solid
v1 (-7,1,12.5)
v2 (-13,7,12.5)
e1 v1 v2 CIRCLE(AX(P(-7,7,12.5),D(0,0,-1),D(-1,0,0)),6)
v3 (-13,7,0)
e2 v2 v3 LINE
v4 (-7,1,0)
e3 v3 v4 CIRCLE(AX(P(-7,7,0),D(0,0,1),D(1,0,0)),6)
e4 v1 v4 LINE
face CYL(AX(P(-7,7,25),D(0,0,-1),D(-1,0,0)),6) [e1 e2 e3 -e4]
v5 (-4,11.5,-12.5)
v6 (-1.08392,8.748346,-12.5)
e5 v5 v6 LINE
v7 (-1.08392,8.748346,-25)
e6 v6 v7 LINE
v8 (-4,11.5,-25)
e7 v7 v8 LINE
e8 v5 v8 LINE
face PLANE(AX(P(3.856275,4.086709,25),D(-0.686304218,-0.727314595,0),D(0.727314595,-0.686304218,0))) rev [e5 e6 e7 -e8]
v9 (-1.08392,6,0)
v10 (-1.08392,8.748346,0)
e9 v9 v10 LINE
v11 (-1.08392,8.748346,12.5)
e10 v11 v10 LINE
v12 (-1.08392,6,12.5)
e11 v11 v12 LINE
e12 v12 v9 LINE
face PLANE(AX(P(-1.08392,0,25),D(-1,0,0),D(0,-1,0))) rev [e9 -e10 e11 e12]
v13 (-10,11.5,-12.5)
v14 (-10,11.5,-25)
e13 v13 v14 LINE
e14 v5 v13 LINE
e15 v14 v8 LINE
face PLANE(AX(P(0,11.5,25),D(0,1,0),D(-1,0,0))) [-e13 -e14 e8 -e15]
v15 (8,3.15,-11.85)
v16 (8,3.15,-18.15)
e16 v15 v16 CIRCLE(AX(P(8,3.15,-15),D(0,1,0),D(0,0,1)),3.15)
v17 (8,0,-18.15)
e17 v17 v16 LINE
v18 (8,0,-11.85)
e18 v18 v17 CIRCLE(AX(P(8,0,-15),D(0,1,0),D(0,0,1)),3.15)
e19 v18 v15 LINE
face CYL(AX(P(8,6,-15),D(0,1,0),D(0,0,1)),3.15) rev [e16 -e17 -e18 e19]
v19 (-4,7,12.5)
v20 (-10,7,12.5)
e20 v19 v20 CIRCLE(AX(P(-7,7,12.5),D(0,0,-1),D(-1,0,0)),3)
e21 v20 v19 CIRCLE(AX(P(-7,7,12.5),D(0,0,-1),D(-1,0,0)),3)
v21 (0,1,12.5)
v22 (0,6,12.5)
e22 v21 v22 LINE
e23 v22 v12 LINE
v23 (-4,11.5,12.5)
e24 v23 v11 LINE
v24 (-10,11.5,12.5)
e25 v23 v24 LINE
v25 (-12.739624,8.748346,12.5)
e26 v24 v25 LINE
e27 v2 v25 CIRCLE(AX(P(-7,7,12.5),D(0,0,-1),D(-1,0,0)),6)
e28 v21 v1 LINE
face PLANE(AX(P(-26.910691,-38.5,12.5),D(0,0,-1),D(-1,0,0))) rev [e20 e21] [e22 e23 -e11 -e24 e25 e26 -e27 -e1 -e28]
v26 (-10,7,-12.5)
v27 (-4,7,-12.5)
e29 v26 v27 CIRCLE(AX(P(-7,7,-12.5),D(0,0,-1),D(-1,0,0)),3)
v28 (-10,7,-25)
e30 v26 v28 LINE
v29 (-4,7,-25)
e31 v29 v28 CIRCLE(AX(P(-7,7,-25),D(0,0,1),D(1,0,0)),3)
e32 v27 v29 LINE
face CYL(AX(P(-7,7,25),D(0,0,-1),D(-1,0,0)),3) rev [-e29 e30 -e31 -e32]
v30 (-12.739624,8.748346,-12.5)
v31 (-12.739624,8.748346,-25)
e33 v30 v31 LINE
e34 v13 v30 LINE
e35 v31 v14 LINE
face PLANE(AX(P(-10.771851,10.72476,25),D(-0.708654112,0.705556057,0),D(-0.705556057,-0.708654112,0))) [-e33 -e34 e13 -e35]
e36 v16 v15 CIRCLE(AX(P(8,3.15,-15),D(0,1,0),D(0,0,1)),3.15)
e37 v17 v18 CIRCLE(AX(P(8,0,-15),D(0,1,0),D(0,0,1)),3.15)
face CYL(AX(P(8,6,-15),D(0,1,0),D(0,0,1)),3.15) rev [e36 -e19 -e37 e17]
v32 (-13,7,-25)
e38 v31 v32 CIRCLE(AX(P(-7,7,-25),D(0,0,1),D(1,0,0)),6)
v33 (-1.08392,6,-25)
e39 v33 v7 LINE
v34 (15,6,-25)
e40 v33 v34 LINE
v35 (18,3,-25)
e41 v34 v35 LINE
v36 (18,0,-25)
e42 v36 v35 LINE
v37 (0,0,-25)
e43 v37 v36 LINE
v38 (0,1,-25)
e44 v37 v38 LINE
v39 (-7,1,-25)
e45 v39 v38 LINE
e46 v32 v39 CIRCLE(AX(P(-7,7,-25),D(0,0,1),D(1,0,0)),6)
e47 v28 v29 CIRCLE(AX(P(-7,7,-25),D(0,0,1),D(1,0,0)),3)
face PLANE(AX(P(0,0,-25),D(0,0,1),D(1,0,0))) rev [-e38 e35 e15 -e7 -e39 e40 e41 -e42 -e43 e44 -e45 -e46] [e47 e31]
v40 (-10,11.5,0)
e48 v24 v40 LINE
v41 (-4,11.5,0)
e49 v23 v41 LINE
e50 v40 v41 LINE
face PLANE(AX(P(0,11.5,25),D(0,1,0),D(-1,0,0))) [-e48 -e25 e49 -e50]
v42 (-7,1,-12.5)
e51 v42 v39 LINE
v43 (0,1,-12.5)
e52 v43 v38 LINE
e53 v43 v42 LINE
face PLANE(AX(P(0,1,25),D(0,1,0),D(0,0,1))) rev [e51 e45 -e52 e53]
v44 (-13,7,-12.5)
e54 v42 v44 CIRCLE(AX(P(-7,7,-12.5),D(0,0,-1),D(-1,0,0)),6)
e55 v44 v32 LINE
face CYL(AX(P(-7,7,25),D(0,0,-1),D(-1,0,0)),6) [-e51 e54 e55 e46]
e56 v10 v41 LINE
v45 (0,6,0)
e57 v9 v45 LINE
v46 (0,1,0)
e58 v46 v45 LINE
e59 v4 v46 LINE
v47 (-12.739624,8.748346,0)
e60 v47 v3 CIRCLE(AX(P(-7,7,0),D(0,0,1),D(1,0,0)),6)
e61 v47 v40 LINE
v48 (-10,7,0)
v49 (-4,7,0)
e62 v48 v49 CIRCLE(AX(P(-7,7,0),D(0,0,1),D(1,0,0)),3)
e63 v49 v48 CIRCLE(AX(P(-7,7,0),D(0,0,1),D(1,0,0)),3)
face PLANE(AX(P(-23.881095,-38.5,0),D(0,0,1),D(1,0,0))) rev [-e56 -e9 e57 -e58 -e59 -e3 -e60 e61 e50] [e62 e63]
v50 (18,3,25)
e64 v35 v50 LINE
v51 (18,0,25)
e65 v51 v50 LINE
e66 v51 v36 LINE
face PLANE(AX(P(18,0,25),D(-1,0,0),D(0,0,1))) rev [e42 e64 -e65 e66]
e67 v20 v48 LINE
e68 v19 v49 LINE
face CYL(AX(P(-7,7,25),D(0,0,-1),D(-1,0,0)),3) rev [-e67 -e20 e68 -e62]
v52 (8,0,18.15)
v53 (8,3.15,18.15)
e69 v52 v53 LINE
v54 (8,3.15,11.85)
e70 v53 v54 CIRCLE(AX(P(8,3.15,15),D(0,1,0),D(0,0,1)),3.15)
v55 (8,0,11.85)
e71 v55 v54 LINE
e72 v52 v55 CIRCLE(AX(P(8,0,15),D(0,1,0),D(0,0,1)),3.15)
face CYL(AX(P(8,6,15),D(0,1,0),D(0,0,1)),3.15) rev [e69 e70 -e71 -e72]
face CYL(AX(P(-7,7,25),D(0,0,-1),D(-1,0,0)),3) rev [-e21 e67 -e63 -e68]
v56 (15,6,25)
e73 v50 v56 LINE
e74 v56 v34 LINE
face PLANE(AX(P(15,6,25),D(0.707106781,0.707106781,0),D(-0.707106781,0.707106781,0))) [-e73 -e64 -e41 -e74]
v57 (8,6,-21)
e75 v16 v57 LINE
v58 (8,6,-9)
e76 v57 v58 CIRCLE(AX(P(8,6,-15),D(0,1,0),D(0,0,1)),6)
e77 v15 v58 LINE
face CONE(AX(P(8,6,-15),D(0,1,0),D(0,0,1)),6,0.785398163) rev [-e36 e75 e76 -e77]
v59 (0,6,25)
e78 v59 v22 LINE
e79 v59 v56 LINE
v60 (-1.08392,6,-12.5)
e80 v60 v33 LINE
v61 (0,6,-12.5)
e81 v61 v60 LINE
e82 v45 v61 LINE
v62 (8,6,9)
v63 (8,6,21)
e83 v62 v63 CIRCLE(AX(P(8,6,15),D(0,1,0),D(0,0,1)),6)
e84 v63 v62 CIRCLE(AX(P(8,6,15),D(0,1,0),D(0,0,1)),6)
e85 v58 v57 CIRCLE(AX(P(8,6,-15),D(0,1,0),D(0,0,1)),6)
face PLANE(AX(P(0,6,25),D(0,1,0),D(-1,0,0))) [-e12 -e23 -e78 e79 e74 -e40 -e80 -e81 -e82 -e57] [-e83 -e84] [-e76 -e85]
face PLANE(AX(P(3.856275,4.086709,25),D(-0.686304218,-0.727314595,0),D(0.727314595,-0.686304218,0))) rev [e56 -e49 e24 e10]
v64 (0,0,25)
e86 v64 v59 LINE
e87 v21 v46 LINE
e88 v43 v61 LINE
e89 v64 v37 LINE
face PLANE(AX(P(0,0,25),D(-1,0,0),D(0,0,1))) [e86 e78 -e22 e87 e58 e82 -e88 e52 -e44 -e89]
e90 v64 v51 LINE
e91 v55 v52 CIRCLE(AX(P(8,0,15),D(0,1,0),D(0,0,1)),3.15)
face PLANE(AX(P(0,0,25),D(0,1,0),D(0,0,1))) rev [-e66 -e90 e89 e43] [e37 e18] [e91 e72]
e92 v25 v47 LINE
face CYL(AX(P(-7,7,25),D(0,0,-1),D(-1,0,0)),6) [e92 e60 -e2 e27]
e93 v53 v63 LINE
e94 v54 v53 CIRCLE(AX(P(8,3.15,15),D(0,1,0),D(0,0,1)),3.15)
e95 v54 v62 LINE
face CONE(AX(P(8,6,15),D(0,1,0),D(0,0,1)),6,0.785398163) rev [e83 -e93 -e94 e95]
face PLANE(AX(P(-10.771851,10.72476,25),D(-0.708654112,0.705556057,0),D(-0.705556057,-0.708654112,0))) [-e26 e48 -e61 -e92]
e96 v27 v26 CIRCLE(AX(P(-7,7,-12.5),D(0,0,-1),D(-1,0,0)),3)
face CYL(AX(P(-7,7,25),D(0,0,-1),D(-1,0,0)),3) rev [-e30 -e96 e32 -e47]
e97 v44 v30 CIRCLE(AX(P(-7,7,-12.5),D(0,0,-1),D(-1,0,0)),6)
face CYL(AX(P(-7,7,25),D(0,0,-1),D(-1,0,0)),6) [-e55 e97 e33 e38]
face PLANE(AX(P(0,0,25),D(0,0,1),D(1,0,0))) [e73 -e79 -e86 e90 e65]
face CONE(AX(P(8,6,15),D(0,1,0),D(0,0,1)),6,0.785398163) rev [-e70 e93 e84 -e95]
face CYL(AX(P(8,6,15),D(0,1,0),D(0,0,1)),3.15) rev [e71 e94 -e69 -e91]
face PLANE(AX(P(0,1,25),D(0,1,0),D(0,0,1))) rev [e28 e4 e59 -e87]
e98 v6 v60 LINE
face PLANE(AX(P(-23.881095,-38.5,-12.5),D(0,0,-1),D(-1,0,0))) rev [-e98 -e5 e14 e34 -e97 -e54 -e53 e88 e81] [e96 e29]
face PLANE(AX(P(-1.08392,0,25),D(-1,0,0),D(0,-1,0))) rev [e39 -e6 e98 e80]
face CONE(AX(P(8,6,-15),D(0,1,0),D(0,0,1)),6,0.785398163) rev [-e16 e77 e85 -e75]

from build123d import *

# Parameters (mm, degrees)
SKETCH_1_R                = 3
EXTRUDE_1_DEPTH           = 25
CHAMFER_1_SIZE            = 3
SKETCH_2_R                = 1.072137289
CUT_EXTRUDE_1_DEPTH       = 50
HOLE_WIZARD_1_D           = 6.3
HOLE_WIZARD_1_CSINK_D     = 12
HOLE_WIZARD_1_CSINK_ANGLE = 90
SKETCH_4_W                = 23.881095176
SKETCH_4_H                = 12.5
SKETCH_4_W_2              = 26.910691004
CUT_EXTRUDE_2_DEPTH       = 50


with BuildPart() as part:
    # 草图1 → 拉伸1 (new, symmetric)
    with BuildSketch(Plane.XY):
        with BuildLine():
            Line((-7, 1), (0, 1))
            Line((0, 1), (0, 0))
            Line((0, 0), (18, 0))
            Line((18, 0), (18, 6))
            Line((18, 6), (-1.083920217, 6))
            Line((-1.083920217, 6), (-1.083920217, 8.748346358))
            Line((-1.083920217, 8.748346358), (-4, 11.5))
            Line((-4, 11.5), (-10, 11.5))
            Line((-10, 11.5), (-12.739624118, 8.748346358))
            ThreePointArc((-12.739624118, 8.748346358), (-11.821310929, 3.428591185), (-7, 1))
        make_face()
        with Locations((-7, 7)):
            Circle(SKETCH_1_R, mode=Mode.SUBTRACT)
    extrude(amount=EXTRUDE_1_DEPTH, both=True)

    # 倒角1
    chamfer_1_edges = [part.edges().sort_by_distance(p)[0] for p in [
        (18, 6, 0),
    ]]
    chamfer(chamfer_1_edges, length=CHAMFER_1_SIZE)

    # 草图2 → 切除-拉伸1 (cut)
    with BuildSketch(Plane(origin=(0, 6, 0), x_dir=(1, 0, 0), z_dir=(0, 1, 0))):
        with Locations(Location((8, 15, 0), (0, 0, 180))):
            Circle(SKETCH_2_R)
        with Locations(Location((8, -15, 0), (0, 0, 270))):
            Circle(SKETCH_2_R)
    extrude(amount=-CUT_EXTRUDE_1_DEPTH, mode=Mode.SUBTRACT)

    # 打孔尺寸开槽半沉头螺钉的类型1 (through all)
    with Locations(Plane(origin=(8, 6, -15), x_dir=(1, 0, 0), z_dir=(0, 1, 0))):
        with Locations((0, 0), (0, -30)):
            CounterSinkHole(HOLE_WIZARD_1_D / 2, HOLE_WIZARD_1_CSINK_D / 2, counter_sink_angle=HOLE_WIZARD_1_CSINK_ANGLE)

    # 草图4 → 切除-拉伸2 (cut)
    with BuildSketch(Plane(origin=(0, 11.5, 0), x_dir=(1, 0, 0), z_dir=(0, 1, 0))):
        with Locations((-11.940547588, 6.25)):
            Rectangle(SKETCH_4_W, SKETCH_4_H)
        with Locations((-13.455345502, -18.75)):
            Rectangle(SKETCH_4_W_2, SKETCH_4_H)
    extrude(amount=-CUT_EXTRUDE_2_DEPTH, mode=Mode.SUBTRACT)


solid = part.part
